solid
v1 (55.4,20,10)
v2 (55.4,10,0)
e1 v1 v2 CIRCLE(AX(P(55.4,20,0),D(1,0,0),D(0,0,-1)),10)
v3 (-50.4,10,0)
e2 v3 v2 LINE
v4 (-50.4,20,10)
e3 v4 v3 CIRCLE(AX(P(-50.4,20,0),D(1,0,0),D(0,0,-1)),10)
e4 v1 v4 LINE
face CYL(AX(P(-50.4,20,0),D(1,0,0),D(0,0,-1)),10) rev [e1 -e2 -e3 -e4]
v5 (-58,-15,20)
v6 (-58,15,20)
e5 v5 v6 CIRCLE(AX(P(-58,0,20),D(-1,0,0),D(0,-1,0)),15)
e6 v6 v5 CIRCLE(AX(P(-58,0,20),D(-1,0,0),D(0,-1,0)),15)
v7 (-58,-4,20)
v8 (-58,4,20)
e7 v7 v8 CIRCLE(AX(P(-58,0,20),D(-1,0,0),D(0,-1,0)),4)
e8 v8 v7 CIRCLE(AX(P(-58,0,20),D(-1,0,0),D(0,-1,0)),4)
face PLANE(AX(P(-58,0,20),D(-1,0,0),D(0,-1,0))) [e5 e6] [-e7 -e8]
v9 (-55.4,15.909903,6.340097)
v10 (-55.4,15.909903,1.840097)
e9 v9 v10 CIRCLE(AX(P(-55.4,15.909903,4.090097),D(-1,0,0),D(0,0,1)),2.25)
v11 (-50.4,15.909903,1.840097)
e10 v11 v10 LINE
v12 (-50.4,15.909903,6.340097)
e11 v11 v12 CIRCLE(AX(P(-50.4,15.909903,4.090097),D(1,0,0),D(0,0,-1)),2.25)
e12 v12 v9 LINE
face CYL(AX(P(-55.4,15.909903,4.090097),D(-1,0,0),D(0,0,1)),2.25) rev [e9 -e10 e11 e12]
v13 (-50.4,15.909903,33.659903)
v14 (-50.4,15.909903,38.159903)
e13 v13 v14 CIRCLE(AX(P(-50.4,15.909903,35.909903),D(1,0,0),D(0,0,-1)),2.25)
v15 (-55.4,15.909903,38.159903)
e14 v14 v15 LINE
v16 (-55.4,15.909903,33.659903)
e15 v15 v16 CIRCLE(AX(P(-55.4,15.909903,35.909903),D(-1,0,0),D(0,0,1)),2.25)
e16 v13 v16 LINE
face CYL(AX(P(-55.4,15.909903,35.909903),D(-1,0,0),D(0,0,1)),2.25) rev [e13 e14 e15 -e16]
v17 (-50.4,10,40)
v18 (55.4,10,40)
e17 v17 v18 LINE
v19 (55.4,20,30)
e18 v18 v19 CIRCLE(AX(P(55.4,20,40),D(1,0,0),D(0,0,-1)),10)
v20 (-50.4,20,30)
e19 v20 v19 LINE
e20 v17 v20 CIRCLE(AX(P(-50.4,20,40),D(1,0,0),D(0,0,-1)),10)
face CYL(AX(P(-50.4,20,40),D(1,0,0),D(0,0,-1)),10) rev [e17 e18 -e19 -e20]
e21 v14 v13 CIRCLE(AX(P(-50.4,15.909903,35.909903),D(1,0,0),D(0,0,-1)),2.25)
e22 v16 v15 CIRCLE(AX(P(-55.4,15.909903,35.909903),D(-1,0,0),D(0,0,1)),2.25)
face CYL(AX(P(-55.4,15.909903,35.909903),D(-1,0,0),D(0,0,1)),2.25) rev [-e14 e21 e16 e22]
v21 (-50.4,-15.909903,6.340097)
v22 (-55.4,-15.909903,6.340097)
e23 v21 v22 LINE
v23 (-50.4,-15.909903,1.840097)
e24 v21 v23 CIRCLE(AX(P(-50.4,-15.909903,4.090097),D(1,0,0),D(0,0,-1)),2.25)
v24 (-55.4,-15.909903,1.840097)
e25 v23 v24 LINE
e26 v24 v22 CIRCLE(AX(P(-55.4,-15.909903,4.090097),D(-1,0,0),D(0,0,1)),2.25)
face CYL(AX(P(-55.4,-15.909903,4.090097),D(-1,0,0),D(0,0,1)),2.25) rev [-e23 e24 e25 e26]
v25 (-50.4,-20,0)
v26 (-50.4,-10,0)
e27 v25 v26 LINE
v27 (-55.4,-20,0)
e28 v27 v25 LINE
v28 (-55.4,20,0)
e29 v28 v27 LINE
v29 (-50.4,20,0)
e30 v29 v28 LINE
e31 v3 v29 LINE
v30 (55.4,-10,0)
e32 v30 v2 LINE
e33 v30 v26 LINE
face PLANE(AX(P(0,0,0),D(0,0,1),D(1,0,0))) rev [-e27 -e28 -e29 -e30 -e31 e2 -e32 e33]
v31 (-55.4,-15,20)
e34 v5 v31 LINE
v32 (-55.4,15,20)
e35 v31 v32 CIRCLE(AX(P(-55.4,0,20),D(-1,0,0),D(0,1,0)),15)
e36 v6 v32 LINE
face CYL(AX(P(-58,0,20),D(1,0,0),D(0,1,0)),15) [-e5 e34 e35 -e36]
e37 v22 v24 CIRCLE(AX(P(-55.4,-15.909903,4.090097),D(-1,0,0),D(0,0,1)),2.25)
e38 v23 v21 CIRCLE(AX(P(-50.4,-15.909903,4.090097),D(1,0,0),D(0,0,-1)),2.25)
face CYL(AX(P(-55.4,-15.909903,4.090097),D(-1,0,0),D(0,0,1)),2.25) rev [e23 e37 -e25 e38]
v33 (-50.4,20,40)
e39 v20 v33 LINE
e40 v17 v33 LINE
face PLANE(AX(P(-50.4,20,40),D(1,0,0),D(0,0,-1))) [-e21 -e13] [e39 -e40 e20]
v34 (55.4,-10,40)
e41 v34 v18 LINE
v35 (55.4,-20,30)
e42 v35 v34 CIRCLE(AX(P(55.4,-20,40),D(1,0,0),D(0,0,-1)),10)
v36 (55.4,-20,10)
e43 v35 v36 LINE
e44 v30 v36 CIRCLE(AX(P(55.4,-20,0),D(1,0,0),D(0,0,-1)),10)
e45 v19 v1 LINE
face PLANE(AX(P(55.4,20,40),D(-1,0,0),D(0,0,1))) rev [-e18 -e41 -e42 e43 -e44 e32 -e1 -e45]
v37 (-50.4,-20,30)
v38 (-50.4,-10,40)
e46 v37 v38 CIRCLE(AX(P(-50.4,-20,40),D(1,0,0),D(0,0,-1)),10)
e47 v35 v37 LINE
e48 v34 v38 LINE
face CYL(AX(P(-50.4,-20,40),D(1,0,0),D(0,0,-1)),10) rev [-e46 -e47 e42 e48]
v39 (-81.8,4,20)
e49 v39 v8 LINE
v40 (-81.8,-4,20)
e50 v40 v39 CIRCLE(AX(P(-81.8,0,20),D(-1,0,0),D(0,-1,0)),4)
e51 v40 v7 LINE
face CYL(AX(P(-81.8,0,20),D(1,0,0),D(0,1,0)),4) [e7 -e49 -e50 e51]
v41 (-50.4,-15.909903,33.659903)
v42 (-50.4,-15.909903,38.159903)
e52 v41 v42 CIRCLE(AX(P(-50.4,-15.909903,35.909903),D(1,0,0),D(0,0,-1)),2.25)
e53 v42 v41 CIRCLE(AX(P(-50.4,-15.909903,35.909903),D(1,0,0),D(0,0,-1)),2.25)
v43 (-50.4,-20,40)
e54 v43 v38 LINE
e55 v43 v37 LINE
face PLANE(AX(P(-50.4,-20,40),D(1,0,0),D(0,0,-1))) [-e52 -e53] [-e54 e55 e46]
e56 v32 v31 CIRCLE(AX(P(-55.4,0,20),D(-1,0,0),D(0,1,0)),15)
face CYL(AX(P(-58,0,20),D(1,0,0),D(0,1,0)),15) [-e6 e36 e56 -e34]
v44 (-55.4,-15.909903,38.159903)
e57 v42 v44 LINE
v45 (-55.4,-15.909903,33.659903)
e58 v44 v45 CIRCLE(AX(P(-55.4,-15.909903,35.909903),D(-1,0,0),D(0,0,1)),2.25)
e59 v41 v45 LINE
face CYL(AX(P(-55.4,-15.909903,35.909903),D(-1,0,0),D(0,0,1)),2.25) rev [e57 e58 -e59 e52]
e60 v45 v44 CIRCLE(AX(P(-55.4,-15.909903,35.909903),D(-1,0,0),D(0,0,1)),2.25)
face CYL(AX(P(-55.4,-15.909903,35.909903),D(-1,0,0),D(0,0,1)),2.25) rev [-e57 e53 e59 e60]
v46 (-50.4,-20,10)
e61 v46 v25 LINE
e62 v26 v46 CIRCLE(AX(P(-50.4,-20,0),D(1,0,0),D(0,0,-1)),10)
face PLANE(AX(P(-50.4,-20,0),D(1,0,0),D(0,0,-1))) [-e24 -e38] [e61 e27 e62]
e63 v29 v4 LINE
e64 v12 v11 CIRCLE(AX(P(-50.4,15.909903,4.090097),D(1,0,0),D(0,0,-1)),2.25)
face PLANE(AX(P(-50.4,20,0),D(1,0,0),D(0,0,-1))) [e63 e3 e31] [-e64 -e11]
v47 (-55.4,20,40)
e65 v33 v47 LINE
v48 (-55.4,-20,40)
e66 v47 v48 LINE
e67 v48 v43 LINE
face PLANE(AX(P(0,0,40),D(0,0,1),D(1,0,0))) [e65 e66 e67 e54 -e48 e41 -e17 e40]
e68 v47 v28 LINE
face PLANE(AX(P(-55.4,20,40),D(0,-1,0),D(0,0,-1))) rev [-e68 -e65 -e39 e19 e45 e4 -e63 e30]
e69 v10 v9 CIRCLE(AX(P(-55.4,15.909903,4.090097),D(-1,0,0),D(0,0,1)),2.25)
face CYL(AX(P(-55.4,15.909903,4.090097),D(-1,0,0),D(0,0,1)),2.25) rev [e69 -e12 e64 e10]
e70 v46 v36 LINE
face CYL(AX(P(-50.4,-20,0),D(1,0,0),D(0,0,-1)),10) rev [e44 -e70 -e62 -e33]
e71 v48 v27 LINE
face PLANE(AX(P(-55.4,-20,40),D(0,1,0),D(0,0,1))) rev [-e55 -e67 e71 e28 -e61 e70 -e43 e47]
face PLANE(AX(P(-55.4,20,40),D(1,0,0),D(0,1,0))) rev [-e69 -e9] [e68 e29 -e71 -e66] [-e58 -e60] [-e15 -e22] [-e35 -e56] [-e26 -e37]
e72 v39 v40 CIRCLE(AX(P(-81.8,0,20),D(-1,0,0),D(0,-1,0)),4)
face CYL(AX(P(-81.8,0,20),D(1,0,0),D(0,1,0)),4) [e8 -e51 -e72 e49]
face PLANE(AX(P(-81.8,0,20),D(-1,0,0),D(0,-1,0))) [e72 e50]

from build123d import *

# Parameters (mm, degrees)
SKETCH1_W           = 110.8
SKETCH1_H           = 40
BOSS_EXTRUDE1_DEPTH = 40
SKETCH2_R           = 15
BOSS_EXTRUDE2_DEPTH = 2.6
SKETCH3_R           = 4
BOSS_EXTRUDE3_DEPTH = 23.8
SKETCH4_R           = 10
CUT_EXTRUDE1_DEPTH  = 105.8
CIRPATTERN1_COUNT   = 4


with BuildPart() as part:
    # Sketch1 → Boss-Extrude1 (new body)
    with BuildSketch(Plane.XY):
        Rectangle(SKETCH1_W, SKETCH1_H)
    extrude(amount=BOSS_EXTRUDE1_DEPTH)

    # Sketch2 → Boss-Extrude2 (add)
    with BuildSketch(Plane.ZY.offset(55.4)):
        with Locations(Location((20, 0, 0), (0, 0, 90))):
            Circle(SKETCH2_R)
    extrude(amount=BOSS_EXTRUDE2_DEPTH)

    # Sketch3 → Boss-Extrude3 (add)
    with BuildSketch(Plane.ZY.offset(58)):
        with Locations(Location((20, 0, 0), (0, 0, 270))):
            Circle(SKETCH3_R)
    extrude(amount=BOSS_EXTRUDE3_DEPTH)

    # Sketch4 → Cut-Extrude1 (cut)
    with BuildSketch(Plane(origin=(55.4, 0, 0), x_dir=(0, 0, -1), z_dir=(1, 0, 0))):
        with Locations((-40, 20)):
            Circle(SKETCH4_R)
        with Locations((0, 20)):
            Circle(SKETCH4_R)
        with Locations((-40, -20)):
            Circle(SKETCH4_R)
        with Locations((0, -20)):
            Circle(SKETCH4_R)
    extrude(amount=-CUT_EXTRUDE1_DEPTH, mode=Mode.SUBTRACT)

    # Sketch5 → M4 Clearance Hole1 (revolve, cut)
    with BuildSketch(Plane(origin=(-55.4, 15.909902577, 4.090097423), x_dir=(0, 0, 1), z_dir=(0, 1, 0))):
        Polygon((0, 0), (0, 258.851936393), (2.25, 257.5), (2.25, 0), align=None)
    m4_clearance_hole1 = revolve(axis=Axis((-61.75, 15.909902577, 4.090097423), (1, 0, 0)), mode=Mode.SUBTRACT)

    # CirPattern1: M4 Clearance Hole1 ×4 about axis
    cirpattern1_axis = Axis((0, 0, 20), (1, 0, 0))
    for i in range(1, CIRPATTERN1_COUNT):
        add(m4_clearance_hole1.rotate(cirpattern1_axis, i * 360 / CIRPATTERN1_COUNT), mode=Mode.SUBTRACT)


solid = part.part
